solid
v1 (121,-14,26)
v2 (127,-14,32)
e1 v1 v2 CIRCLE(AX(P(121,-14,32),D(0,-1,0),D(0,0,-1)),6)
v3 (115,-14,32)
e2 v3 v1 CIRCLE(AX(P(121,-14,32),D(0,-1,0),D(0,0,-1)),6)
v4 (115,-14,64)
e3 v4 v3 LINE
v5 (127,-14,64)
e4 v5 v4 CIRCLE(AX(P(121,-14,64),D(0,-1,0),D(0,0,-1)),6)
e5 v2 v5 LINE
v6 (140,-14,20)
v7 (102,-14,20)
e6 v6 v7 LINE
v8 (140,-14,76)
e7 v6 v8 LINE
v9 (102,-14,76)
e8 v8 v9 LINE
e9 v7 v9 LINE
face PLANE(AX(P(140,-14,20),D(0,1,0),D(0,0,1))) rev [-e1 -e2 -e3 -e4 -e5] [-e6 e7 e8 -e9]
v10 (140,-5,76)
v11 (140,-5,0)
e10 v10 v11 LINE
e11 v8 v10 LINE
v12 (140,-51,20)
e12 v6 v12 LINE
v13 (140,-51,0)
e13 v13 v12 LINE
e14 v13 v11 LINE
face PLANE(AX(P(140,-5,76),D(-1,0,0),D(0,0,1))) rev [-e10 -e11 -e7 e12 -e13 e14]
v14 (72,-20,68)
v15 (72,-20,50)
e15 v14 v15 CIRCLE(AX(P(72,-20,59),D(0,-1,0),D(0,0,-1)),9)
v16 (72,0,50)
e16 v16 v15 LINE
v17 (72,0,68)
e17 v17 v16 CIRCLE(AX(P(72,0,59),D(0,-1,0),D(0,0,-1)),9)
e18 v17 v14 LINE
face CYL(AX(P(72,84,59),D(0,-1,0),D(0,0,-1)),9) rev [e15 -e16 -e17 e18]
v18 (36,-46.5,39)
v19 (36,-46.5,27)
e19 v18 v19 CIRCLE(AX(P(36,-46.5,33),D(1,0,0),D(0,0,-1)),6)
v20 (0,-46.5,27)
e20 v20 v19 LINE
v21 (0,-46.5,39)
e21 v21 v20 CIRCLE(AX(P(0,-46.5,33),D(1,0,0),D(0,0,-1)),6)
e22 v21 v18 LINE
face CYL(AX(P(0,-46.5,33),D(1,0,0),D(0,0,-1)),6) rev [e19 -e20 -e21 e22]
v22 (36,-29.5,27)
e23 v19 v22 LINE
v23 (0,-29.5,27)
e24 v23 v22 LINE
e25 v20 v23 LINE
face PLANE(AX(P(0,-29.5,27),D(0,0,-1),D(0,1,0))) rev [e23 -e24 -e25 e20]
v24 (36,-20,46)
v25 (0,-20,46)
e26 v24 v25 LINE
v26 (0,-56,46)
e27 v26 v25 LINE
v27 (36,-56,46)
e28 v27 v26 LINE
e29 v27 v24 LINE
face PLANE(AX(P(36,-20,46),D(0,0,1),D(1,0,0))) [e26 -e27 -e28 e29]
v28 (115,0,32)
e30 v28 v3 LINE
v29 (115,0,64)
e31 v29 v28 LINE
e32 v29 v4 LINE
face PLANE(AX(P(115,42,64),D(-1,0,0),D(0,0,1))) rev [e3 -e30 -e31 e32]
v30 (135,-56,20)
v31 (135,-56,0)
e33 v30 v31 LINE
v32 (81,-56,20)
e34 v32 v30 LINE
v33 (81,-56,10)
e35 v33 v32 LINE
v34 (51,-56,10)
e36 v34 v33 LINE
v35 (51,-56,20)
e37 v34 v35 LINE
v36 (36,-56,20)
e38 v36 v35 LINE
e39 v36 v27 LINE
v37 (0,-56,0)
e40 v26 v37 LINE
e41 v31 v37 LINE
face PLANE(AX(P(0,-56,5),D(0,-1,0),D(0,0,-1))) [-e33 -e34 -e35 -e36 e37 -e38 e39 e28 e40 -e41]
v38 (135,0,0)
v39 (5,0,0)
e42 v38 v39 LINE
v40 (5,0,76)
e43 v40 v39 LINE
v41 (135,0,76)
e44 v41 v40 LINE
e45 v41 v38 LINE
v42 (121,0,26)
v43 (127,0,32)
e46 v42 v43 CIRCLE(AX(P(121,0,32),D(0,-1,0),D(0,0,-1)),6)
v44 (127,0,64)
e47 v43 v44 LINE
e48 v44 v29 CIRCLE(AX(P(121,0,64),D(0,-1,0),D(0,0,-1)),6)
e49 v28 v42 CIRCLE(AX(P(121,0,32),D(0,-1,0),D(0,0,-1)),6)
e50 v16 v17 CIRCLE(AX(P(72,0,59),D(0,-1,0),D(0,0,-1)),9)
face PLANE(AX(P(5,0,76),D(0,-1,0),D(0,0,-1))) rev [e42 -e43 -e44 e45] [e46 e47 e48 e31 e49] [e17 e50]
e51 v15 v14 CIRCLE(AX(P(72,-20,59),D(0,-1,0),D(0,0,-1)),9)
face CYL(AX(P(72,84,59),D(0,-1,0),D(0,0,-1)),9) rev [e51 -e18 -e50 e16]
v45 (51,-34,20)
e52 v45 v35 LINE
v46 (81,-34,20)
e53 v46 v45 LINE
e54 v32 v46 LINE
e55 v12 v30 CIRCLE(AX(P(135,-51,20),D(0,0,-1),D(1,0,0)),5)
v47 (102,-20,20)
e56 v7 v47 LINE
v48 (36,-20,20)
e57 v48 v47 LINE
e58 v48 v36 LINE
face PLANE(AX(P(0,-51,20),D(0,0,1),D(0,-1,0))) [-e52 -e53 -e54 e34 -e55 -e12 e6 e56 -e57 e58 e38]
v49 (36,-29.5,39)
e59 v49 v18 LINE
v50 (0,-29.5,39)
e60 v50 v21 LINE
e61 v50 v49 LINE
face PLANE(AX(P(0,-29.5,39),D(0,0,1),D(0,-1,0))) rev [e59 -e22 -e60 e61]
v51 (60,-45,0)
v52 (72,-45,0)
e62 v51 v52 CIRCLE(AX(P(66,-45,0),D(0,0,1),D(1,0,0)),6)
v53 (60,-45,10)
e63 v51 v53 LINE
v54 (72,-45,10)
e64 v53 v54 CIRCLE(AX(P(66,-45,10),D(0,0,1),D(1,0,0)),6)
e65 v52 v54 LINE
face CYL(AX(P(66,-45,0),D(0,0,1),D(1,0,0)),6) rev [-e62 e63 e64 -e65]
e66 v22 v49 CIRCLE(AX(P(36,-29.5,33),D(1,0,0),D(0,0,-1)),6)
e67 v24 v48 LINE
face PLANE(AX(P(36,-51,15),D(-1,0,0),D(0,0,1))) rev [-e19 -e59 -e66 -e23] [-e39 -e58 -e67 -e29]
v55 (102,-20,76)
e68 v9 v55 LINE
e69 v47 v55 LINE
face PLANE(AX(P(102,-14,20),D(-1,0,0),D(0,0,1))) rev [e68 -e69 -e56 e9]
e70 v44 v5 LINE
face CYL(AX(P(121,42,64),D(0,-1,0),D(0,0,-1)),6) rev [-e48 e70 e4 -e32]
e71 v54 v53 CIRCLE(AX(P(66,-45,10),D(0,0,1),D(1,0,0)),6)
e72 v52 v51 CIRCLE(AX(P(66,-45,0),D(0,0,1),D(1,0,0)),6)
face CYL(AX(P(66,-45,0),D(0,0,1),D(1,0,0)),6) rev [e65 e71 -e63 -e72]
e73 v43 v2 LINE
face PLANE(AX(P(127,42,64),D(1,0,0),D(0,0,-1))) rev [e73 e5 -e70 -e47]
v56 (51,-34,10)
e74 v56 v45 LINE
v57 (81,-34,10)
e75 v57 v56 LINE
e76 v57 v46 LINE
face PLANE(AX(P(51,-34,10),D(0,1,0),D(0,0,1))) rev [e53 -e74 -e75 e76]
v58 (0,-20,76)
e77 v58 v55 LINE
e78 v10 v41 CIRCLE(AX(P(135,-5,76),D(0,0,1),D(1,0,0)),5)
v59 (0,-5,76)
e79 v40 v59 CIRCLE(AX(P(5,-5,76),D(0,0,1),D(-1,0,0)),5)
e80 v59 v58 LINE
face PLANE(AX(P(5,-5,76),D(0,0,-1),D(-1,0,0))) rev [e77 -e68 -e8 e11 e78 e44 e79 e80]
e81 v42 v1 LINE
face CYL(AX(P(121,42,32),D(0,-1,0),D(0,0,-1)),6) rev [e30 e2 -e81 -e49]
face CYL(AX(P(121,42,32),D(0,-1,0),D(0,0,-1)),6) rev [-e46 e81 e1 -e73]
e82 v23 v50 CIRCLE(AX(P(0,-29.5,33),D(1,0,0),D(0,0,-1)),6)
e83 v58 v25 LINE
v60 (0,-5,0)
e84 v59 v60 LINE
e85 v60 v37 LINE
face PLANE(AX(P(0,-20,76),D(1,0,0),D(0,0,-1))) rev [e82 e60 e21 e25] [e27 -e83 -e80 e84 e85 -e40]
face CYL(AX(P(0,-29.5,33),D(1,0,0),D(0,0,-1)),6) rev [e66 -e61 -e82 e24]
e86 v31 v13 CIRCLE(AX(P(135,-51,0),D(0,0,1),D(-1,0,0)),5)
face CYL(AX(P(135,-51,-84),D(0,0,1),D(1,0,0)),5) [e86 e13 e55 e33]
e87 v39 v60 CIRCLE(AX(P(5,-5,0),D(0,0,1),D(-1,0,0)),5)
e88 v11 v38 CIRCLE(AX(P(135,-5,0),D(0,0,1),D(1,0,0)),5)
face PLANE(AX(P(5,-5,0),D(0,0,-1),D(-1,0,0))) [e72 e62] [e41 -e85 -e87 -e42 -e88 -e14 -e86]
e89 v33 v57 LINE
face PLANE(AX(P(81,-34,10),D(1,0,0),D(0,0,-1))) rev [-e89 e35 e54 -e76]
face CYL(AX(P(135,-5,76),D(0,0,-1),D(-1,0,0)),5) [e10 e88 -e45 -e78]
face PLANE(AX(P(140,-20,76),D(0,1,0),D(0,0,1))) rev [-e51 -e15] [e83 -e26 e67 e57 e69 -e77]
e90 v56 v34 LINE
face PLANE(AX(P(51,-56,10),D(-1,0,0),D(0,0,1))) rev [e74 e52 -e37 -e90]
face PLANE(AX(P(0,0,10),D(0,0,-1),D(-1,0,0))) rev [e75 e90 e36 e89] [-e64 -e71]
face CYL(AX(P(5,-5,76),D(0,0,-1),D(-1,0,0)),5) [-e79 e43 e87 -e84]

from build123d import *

# Parameters (mm, degrees)
BASE_PLATE_DEPTH             = 76
SIDE_WALL_DEPTH              = 140
POCKET_PROFILE_W             = 38
POCKET_PROFILE_H             = 6
POCKET_CUT_DEPTH             = 56
SLOT_12X32_DEPTH             = 56
GUIDE_START                  = -36
GUIDE_RIB_DEPTH              = 36
OUTER_START                  = -140
OUTER_CORNER_ROUND_R10_DEPTH = 140
RIB_CORNER_ROUND_R10_DEPTH   = 104
CORNER_RELIEF_R10_DEPTH      = 104
HOLE_18_SKETCH_R             = 9
HOLE_18_DEPTH                = 104
NOTCH_PROFILE_W              = 30
NOTCH_PROFILE_H              = 22
NOTCH_CUT_DEPTH              = 10
HOLE_12_SKETCH_R             = 6
HOLE_12_DEPTH                = 10
RIB_SLOT_12_WIDE_DEPTH       = 36


with BuildPart() as part:
    # Base Plate Profile → Base Plate (new body)
    with BuildSketch(Plane.XY):
        with BuildLine():
            Line((5, 0), (135, 0))
            ThreePointArc((135, 0), (138.535533906, -1.464466094), (140, -5))
            Line((140, -5), (140, -20))
            Line((140, -20), (0, -20))
            Line((0, -20), (0, -5))
            ThreePointArc((0, -5), (1.464466094, -1.464466094), (5, 0))
        make_face()
    extrude(amount=BASE_PLATE_DEPTH)

    # Side Wall Profile → Side Wall (add)
    with BuildSketch(Plane(origin=(140, 0, 0), x_dir=(0, 0, -1), z_dir=(1, 0, 0))):
        with BuildLine():
            Line((0, -20), (0, -51))
            ThreePointArc((0, -51), (-1.464466094, -54.535533906), (-5, -56))
            Line((-5, -56), (-15, -56))
            ThreePointArc((-15, -56), (-18.535533906, -54.535533906), (-20, -51))
            Line((-20, -51), (-20, -20))
            Line((-20, -20), (0, -20))
        make_face()
    extrude(amount=-SIDE_WALL_DEPTH)

    # Pocket Profile → Pocket Cut (cut)
    with BuildSketch(Plane.XY.offset(76)):
        with Locations((121, -17)):
            Rectangle(POCKET_PROFILE_W, POCKET_PROFILE_H)
    extrude(amount=-POCKET_CUT_DEPTH, mode=Mode.SUBTRACT)

    # Slot 12x32 Profile → Slot 12x32 (cut)
    with BuildSketch(Plane.XZ.offset(14)):
        with BuildLine():
            Line((115, 64), (115, 32))
            ThreePointArc((115, 32), (121, 26), (127, 32))
            Line((127, 32), (127, 64))
            ThreePointArc((127, 64), (121, 70), (115, 64))
        make_face()
    extrude(amount=-SLOT_12X32_DEPTH, mode=Mode.SUBTRACT)

    # Guide Rib Profile → Guide Rib (add)
    with BuildSketch(Plane.ZY.offset(GUIDE_START)):
        with BuildLine():
            Line((20, -20), (46, -20))
            Line((46, -20), (46, -56))
            Line((46, -56), (15, -56))
            ThreePointArc((15, -56), (18.535533906, -54.535533906), (20, -51))
            Line((20, -51), (20, -20))
        make_face()
    extrude(amount=GUIDE_RIB_DEPTH)

    # Outer Corner Round Profile → Outer Corner Round R10 (add)
    with BuildSketch(Plane.ZY.offset(OUTER_START)):
        with BuildLine():
            Line((0, -51), (0, -56))
            Line((0, -56), (5, -56))
            ThreePointArc((5, -56), (1.464466094, -54.535533906), (0, -51))
        make_face()
    extrude(amount=OUTER_CORNER_ROUND_R10_DEPTH)

    # Rib Corner Round Profile → Rib Corner Round R10 (add)
    with BuildSketch(Plane(origin=(140, 0, 0), x_dir=(0, 0, -1), z_dir=(1, 0, 0))):
        with BuildLine():
            Line((-20, -51), (-20, -56))
            Line((-20, -56), (-15, -56))
            ThreePointArc((-15, -56), (-18.535533906, -54.535533906), (-20, -51))
        make_face()
    extrude(amount=-RIB_CORNER_ROUND_R10_DEPTH)

    # Corner Relief Profile → Corner Relief R10 (cut)
    with BuildSketch(Plane.XY.offset(20)):
        with BuildLine():
            Line((140, -56), (140, -51))
            ThreePointArc((140, -51), (138.535533906, -54.535533906), (135, -56))
            Line((135, -56), (140, -56))
        make_face()
    extrude(amount=-CORNER_RELIEF_R10_DEPTH, mode=Mode.SUBTRACT)

    # Hole Ø18 Sketch → Hole Ø18 (cut)
    with BuildSketch(Plane.XZ.offset(20)):
        with Locations(Location((72, 59, 0), (0, 0, 270))):
            Circle(HOLE_18_SKETCH_R)
    extrude(amount=-HOLE_18_DEPTH, mode=Mode.SUBTRACT)

    # Notch Profile → Notch Cut (cut)
    with BuildSketch(Plane.XY.offset(20)):
        with Locations((66, -45)):
            Rectangle(NOTCH_PROFILE_W, NOTCH_PROFILE_H)
    extrude(amount=-NOTCH_CUT_DEPTH, mode=Mode.SUBTRACT)

    # Hole Ø12 Sketch → Hole Ø12 (cut)
    with BuildSketch(Plane.XY.offset(10)):
        with Locations((66, -45)):
            Circle(HOLE_12_SKETCH_R)
    extrude(amount=-HOLE_12_DEPTH, mode=Mode.SUBTRACT)

    # Rib Slot Profile → Rib Slot 12 Wide (cut)
    with BuildSketch(Plane(origin=(36, 0, 0), x_dir=(0, 0, -1), z_dir=(1, 0, 0))):
        with BuildLine():
            Line((-39, -29.5), (-39, -46.5))
            ThreePointArc((-39, -46.5), (-33, -52.5), (-27, -46.5))
            Line((-27, -46.5), (-27, -29.5))
            ThreePointArc((-27, -29.5), (-33, -23.5), (-39, -29.5))
        make_face()
    extrude(amount=-RIB_SLOT_12_WIDE_DEPTH, mode=Mode.SUBTRACT)


solid = part.part
